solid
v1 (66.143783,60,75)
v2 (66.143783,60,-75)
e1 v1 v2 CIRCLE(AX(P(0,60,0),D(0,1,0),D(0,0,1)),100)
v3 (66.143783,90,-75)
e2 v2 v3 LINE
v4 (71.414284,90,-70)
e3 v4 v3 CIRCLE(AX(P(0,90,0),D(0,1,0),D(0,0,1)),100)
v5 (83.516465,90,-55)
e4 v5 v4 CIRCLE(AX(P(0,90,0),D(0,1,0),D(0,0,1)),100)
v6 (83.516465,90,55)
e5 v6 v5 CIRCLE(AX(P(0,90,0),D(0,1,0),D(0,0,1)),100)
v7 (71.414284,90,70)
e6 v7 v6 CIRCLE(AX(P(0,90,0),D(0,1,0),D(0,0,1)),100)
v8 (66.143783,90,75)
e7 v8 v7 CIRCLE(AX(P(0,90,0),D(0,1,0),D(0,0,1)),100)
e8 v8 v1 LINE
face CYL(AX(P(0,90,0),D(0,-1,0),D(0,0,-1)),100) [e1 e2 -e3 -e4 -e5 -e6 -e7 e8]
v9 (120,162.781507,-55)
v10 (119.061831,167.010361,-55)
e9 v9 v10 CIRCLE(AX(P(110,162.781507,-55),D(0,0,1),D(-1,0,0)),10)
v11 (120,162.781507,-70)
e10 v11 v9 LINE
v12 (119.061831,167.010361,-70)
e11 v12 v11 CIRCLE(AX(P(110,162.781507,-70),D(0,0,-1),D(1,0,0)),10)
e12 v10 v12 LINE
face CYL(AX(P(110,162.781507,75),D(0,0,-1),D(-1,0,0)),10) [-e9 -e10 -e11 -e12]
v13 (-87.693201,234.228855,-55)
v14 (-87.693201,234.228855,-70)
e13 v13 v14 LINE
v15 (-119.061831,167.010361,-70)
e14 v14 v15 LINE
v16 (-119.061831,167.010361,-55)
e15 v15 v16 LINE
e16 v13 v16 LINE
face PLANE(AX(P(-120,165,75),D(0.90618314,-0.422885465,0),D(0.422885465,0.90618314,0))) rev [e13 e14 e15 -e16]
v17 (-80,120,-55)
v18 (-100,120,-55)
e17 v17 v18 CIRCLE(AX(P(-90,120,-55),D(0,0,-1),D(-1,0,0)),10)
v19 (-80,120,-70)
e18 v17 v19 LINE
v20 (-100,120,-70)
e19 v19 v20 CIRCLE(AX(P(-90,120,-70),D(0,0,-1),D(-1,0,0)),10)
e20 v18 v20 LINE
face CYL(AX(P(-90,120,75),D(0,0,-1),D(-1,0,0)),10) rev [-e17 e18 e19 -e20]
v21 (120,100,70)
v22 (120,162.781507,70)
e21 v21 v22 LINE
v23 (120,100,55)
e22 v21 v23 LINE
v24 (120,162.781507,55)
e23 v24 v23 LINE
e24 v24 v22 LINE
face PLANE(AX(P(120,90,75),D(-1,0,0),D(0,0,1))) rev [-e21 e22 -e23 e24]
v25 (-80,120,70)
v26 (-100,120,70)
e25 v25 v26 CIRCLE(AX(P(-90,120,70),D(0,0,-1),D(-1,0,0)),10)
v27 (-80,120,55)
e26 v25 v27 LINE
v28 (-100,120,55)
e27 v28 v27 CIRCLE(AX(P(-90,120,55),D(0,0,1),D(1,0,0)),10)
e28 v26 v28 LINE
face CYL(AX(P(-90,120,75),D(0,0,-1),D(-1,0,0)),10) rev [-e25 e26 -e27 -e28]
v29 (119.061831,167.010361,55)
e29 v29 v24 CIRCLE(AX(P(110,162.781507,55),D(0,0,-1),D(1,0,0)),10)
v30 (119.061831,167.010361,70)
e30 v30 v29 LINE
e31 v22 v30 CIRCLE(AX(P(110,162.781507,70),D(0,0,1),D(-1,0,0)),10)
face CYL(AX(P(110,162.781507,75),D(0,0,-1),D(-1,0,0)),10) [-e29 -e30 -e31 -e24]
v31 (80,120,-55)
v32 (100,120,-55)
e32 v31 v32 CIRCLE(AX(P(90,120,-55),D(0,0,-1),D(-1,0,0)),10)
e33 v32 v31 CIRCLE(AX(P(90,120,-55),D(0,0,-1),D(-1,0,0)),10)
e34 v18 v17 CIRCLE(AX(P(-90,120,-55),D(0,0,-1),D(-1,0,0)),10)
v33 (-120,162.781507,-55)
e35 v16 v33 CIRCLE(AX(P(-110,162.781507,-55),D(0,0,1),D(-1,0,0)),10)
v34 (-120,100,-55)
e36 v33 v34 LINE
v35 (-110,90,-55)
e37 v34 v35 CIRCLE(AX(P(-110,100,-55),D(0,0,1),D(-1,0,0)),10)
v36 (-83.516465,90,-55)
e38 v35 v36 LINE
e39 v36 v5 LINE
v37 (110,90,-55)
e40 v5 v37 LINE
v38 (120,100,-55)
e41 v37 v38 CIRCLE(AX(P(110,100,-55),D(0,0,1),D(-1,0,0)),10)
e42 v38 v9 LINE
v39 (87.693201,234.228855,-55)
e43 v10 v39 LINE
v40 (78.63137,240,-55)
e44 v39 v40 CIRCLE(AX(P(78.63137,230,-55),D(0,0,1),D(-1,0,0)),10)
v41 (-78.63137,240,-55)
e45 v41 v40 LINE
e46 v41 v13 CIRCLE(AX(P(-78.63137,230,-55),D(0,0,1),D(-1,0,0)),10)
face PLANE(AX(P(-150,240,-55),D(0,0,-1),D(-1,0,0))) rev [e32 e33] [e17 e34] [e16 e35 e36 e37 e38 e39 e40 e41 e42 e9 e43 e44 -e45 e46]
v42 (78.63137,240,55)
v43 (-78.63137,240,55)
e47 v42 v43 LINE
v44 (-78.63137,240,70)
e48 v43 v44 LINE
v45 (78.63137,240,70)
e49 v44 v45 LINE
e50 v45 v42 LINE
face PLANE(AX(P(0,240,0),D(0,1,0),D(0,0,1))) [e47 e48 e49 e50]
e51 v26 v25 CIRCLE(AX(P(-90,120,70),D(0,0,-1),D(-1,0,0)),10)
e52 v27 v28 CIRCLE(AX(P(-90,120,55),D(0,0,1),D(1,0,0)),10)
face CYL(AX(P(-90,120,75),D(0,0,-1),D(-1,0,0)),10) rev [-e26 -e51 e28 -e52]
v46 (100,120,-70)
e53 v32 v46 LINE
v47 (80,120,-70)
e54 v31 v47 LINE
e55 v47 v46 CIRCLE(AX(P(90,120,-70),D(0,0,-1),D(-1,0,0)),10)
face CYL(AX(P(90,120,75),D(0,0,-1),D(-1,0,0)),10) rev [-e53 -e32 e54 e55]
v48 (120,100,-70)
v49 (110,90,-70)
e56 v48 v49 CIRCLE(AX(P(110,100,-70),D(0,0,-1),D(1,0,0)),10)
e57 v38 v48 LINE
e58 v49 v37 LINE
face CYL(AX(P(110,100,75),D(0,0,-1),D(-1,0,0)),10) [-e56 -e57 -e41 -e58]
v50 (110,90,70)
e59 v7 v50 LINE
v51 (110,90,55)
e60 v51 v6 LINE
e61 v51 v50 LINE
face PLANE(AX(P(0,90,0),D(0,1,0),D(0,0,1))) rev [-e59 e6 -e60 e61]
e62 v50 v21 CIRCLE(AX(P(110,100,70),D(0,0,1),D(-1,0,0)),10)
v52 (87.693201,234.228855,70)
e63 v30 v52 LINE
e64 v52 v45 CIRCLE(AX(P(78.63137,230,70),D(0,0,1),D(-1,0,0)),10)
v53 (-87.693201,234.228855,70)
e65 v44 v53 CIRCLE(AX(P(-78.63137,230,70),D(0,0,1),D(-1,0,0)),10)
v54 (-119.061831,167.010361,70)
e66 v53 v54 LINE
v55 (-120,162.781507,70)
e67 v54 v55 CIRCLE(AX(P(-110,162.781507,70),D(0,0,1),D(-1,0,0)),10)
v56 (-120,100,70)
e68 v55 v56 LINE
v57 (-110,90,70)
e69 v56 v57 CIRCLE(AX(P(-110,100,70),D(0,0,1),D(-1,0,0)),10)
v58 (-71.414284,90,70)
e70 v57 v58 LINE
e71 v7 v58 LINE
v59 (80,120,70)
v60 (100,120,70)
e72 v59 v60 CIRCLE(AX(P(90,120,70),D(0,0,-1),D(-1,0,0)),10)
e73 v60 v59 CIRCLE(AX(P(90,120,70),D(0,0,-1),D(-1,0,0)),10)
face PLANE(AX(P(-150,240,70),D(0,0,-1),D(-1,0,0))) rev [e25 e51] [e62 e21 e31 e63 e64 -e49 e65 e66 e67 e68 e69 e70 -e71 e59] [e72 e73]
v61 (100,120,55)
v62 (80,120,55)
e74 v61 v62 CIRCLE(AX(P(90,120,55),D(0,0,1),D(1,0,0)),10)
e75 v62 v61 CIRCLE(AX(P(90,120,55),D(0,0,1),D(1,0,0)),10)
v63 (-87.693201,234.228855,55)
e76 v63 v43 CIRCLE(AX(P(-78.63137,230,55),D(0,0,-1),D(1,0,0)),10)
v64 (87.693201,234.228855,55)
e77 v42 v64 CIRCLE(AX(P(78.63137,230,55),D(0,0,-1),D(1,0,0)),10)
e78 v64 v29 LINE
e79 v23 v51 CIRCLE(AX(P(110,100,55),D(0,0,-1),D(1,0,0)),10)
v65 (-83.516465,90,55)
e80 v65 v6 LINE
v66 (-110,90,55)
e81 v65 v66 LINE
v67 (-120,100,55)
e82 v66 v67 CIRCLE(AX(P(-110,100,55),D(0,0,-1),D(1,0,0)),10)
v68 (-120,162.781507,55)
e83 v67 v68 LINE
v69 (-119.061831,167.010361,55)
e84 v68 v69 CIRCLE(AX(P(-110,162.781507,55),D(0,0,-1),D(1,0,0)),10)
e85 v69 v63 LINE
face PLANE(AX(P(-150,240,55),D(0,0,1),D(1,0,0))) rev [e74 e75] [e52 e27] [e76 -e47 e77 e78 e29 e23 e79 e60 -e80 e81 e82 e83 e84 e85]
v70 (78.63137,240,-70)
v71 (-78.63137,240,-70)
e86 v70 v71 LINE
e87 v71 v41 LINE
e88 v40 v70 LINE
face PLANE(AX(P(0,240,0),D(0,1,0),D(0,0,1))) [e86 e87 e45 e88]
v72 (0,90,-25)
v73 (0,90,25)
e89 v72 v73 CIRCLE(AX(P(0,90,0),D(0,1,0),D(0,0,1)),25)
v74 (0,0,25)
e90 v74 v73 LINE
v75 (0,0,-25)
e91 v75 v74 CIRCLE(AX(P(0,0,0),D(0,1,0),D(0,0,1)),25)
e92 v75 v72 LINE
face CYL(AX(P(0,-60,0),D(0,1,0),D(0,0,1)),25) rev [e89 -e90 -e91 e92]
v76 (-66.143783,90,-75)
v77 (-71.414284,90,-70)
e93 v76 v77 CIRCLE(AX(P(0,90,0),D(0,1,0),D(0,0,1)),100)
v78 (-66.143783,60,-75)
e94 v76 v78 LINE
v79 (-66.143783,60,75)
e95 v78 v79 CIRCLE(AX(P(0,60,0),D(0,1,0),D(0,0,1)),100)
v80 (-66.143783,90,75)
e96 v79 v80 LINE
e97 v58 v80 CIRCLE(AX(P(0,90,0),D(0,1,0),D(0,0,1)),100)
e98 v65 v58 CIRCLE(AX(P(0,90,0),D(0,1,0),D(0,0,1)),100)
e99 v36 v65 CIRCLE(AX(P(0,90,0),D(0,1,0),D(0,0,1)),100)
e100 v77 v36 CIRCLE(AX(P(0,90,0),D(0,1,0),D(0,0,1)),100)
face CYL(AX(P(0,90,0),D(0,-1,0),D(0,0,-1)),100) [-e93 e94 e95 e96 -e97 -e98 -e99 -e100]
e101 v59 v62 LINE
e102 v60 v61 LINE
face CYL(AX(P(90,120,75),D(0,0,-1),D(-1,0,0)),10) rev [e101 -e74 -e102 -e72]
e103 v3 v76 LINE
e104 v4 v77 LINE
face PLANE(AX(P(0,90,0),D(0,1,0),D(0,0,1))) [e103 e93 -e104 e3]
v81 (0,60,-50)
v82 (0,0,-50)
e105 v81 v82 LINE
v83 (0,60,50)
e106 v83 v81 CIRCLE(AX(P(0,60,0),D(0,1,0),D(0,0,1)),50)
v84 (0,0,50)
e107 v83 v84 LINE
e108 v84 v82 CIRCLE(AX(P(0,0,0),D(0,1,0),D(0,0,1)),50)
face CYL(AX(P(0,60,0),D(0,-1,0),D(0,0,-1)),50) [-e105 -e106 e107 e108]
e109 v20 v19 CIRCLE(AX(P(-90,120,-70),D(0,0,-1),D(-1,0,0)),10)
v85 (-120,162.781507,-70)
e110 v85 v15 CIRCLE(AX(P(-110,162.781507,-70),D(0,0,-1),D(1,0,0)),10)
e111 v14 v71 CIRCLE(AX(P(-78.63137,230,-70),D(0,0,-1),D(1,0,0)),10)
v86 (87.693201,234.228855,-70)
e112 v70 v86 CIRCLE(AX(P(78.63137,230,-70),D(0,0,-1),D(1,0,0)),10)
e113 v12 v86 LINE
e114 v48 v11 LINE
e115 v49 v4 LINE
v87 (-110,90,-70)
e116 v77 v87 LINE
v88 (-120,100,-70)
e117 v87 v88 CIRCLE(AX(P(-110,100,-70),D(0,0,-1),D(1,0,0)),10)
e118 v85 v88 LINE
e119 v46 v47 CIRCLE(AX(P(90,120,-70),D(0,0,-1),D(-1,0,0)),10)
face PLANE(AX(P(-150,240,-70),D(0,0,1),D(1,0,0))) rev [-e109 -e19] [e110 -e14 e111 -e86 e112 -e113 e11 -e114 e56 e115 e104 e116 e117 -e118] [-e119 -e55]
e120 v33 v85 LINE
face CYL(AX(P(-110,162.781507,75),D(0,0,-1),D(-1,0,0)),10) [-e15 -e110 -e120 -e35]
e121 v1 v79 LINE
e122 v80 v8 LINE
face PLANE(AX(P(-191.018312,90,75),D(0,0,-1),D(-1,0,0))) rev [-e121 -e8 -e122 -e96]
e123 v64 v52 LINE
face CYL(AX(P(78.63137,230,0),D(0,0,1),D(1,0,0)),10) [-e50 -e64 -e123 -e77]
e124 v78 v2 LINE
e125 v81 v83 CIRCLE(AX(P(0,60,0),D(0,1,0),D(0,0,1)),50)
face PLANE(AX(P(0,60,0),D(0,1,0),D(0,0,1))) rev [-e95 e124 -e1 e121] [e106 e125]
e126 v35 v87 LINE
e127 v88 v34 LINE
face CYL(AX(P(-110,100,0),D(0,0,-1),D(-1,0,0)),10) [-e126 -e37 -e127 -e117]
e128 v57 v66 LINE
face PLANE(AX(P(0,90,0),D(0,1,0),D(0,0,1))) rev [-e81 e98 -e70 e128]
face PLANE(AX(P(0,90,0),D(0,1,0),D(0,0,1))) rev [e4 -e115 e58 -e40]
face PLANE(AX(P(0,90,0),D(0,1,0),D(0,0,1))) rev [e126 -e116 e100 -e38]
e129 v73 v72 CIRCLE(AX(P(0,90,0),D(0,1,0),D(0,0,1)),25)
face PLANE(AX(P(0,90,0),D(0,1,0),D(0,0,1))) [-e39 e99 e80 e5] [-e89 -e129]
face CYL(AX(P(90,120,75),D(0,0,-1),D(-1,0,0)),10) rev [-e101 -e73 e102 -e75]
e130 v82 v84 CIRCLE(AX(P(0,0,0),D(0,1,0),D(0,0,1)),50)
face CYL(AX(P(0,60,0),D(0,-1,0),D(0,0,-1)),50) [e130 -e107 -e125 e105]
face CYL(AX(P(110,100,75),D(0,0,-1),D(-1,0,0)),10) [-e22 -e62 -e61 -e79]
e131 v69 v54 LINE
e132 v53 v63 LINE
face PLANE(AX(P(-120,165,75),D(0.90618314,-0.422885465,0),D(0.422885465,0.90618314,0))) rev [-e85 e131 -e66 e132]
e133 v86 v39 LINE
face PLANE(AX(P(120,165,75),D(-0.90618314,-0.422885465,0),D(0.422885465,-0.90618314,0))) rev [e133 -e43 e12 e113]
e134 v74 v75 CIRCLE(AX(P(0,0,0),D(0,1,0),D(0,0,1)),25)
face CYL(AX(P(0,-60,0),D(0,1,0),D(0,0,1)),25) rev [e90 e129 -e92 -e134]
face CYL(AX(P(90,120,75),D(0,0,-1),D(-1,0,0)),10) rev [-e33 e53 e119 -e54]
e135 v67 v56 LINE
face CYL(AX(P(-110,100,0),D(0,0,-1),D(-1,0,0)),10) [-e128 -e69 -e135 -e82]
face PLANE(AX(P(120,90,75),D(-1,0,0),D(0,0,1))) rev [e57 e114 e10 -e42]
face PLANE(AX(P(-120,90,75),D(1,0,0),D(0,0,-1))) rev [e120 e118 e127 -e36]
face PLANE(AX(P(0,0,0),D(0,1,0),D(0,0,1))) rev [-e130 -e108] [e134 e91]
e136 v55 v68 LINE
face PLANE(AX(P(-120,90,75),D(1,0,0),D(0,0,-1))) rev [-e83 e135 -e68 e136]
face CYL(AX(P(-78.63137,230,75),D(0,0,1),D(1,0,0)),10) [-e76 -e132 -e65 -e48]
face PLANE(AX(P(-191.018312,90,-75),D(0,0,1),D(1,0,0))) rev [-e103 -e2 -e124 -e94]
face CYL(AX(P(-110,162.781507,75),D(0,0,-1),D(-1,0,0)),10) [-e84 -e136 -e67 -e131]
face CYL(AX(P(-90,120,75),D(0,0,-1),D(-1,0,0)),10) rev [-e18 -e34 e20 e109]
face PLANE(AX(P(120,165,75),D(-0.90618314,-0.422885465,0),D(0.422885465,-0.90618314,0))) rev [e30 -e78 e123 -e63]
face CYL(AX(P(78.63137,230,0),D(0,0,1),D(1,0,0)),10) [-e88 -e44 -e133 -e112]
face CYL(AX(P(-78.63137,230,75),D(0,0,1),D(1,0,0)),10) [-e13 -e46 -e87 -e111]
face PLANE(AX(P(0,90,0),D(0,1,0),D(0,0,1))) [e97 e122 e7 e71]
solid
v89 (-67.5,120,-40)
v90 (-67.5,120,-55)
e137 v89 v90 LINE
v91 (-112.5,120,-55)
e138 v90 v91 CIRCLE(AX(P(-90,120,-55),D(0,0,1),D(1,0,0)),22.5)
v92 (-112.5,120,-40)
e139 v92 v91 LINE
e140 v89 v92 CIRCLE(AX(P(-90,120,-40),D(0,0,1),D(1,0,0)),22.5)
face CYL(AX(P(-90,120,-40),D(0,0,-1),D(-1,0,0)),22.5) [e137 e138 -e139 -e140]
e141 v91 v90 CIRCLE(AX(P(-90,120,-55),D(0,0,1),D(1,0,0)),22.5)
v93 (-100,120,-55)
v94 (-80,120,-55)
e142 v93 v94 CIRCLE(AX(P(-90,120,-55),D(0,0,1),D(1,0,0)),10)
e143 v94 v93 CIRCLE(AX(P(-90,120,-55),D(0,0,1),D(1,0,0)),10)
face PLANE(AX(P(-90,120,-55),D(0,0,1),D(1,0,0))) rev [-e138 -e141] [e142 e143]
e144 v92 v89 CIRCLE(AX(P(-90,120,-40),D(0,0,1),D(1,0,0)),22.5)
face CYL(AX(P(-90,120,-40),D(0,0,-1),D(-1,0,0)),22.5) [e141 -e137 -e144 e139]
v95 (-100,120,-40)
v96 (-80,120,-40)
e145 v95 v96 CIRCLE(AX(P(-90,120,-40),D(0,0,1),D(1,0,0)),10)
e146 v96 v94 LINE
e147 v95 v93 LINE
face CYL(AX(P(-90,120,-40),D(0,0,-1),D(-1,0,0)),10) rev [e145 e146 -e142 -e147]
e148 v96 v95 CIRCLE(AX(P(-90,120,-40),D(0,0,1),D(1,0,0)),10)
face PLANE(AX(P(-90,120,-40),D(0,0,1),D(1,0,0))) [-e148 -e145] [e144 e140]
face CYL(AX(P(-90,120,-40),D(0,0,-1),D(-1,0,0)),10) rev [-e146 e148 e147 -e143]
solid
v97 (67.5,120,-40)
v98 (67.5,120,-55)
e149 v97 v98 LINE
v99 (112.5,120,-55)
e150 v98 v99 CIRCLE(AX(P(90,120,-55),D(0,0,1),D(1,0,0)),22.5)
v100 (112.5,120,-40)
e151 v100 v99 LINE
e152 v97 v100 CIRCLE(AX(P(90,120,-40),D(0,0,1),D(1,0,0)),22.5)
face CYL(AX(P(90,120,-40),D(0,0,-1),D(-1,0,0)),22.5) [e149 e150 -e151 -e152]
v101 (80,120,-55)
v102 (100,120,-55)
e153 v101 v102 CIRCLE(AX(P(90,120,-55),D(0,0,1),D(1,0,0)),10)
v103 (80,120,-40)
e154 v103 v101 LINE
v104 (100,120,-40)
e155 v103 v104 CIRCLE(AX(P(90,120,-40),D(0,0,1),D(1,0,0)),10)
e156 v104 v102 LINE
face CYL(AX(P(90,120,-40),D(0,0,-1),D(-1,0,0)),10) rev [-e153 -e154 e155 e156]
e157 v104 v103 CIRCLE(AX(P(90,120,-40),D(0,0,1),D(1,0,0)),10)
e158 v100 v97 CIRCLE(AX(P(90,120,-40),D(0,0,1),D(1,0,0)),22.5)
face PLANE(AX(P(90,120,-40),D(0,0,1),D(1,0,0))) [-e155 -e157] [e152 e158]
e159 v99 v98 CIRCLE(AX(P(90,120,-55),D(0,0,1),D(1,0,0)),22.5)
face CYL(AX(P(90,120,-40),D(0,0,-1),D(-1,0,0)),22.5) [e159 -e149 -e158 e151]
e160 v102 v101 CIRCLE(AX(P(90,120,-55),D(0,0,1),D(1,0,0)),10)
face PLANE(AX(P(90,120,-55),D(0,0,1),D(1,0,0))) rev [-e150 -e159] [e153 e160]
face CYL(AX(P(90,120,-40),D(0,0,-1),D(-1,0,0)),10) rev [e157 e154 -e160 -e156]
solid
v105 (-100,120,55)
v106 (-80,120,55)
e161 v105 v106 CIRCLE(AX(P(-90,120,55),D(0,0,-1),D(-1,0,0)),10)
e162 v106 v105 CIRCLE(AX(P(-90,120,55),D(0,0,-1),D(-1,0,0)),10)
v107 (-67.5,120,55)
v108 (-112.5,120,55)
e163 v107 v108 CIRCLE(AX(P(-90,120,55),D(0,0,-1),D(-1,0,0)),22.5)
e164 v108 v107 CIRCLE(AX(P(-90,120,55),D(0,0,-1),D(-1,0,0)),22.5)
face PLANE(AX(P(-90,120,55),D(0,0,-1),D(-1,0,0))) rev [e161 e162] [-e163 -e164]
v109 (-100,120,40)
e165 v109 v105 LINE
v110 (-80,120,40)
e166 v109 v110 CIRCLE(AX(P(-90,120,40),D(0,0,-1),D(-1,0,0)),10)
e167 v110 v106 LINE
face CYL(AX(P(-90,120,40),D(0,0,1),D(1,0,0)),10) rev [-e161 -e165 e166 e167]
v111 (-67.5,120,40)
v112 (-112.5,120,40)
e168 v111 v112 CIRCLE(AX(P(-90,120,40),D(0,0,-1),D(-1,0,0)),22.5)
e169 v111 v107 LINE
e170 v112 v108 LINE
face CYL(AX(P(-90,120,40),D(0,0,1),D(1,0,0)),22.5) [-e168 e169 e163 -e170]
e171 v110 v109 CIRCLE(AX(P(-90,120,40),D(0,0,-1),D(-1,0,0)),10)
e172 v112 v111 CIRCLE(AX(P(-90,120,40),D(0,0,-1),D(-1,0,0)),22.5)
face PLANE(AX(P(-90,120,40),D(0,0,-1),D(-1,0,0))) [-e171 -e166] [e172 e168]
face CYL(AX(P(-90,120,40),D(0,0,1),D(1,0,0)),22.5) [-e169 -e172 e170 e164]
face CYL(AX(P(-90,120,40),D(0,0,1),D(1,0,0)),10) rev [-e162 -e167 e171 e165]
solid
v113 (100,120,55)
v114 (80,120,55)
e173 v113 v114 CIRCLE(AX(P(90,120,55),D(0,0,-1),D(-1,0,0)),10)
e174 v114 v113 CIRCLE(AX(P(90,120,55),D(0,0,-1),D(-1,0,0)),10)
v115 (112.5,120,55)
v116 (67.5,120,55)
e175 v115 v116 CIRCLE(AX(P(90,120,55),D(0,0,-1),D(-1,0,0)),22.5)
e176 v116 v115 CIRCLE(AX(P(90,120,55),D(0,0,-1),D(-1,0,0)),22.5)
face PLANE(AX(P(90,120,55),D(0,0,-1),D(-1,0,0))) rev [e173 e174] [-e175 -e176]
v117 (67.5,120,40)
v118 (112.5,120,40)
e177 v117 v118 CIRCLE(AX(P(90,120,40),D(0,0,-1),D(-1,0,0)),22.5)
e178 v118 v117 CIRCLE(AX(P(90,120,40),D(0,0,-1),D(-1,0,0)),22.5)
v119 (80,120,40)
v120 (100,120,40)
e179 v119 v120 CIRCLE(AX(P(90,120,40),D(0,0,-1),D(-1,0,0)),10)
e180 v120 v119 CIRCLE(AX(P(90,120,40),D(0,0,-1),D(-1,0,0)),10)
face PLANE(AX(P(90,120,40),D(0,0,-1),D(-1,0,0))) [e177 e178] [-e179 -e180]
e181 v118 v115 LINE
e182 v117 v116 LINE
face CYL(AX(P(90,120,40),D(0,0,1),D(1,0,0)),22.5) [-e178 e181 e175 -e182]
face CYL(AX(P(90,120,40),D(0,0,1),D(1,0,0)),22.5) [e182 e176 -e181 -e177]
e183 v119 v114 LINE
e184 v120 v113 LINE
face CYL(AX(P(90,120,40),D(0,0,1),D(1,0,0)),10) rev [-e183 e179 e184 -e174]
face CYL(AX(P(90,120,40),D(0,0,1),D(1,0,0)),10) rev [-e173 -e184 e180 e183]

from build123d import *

# Parameters (mm, degrees)
SKETCH1_R             = 50
BOSS_EXTRUDE1_DEPTH   = 60
SKETCH2_R             = 100
BOSS_EXTRUDE2_DEPTH   = 30
CUT_EXTRUDE1_DEPTH    = 154.622914957
SKETCH4_W             = 300
SKETCH4_H             = 15
BOSS_EXTRUDE3_DEPTH   = 150
SKETCH5_W             = 30
SKETCH5_H             = 150
CUT_EXTRUDE2_DEPTH    = 319.001572323
FILLET1_R             = 10
SKETCH6_R             = 25
CUT_EXTRUDE3_DEPTH    = 150
SKETCH7_R             = 10
CUT_EXTRUDE4_DEPTH    = 306
SKETCH8_R             = 22.5
SKETCH8_R_2           = 10
BOSS_EXTRUDE4_DEPTH   = 15
BOSS_EXTRUDE4_2_DEPTH = 15
SKETCH9_R             = 22.5
SKETCH9_R_2           = 10
BOSS_EXTRUDE5_DEPTH   = 15
BOSS_EXTRUDE5_2_DEPTH = 15
CUT_EXTRUDE5_DEPTH    = 306
FILLET2_R             = 10


with BuildPart() as part:
    # Sketch1 → Boss-Extrude1 (new body)
    with BuildSketch(Plane(origin=(0, 0, 0), x_dir=(1, 0, 0), z_dir=(0, 1, 0))):
        with Locations(Location((0, 0, 0), (0, 0, 270))):
            Circle(SKETCH1_R)
    extrude(amount=BOSS_EXTRUDE1_DEPTH)

    # Sketch2 → Boss-Extrude2 (add)
    with BuildSketch(Plane(origin=(0, 60, 0), x_dir=(1, 0, 0), z_dir=(0, 1, 0))):
        with Locations(Location((0, 0, 0), (0, 0, 270))):
            Circle(SKETCH2_R)
    extrude(amount=BOSS_EXTRUDE2_DEPTH)

    # Sketch3 → Cut-Extrude1 (cut, through all)
    with BuildSketch(Plane.XZ.offset(-60)):
        Polygon((191.018311805, 75), (5.81663556, 170.543754632), (-191.018311805, 75), align=None)
        Polygon((-191.018311805, -75), (191.018311805, -75), (12.796598233, -157.049160132), align=None)
    extrude(amount=-CUT_EXTRUDE1_DEPTH, mode=Mode.SUBTRACT)

    # Sketch4 → Boss-Extrude3 (add)
    with BuildSketch(Plane(origin=(0, 90, 0), x_dir=(1, 0, 0), z_dir=(0, 1, 0))):
        with Locations((0, 62.5)):
            Rectangle(SKETCH4_W, SKETCH4_H)
        with Locations((0, -62.5)):
            Rectangle(SKETCH4_W, SKETCH4_H)
    extrude(amount=BOSS_EXTRUDE3_DEPTH)

    # Sketch5 → Cut-Extrude2 (cut, through all)
    with BuildSketch(Plane(origin=(0, 0, -70), x_dir=(-1, 0, 0), z_dir=(0, 0, -1))):
        with Locations((-135, 165)):
            Rectangle(SKETCH5_W, SKETCH5_H)
        with Locations((135, 165)):
            Rectangle(SKETCH5_W, SKETCH5_H)
    extrude(amount=-CUT_EXTRUDE2_DEPTH, mode=Mode.SUBTRACT)

    # Fillet1
    fillet1_edges = [part.edges().sort_by_distance(p)[0] for p in [
        (-120, 240, -62.5),
        (-120, 240, 62.5),
        (-120, 90, -62.5),
        (-120, 90, 62.5),
        (120, 240, 62.5),
        (120, 90, -62.5),
        (120, 90, 62.5),
        (120, 240, -62.5),
    ]]
    fillet(fillet1_edges, radius=FILLET1_R)

    # Sketch6 → Cut-Extrude3 (cut)
    with BuildSketch(Plane(origin=(0, 90, 0), x_dir=(1, 0, 0), z_dir=(0, 1, 0))):
        with Locations(Location((0, 0, 0), (0, 0, 270))):
            Circle(SKETCH6_R)
    extrude(amount=-CUT_EXTRUDE3_DEPTH, mode=Mode.SUBTRACT)

    # Sketch7 → Cut-Extrude4 (cut, through all)
    with BuildSketch(Plane(origin=(0, 0, -70), x_dir=(-1, 0, 0), z_dir=(0, 0, -1))):
        with Locations((-90, 120)):
            Circle(SKETCH7_R)
        with Locations((90, 120)):
            Circle(SKETCH7_R)
    extrude(amount=-CUT_EXTRUDE4_DEPTH, mode=Mode.SUBTRACT)

    # Sketch10 → Cut-Extrude5 (cut, through all)
    with BuildSketch(Plane(origin=(0, 0, -70), x_dir=(-1, 0, 0), z_dir=(0, 0, -1))):
        Polygon((-120, 165), (-85, 240), (-120, 240), align=None)
        Polygon((120, 165), (85, 240), (120, 240), align=None)
    extrude(amount=-CUT_EXTRUDE5_DEPTH, mode=Mode.SUBTRACT)

    # Fillet2
    fillet2_edges = [part.edges().sort_by_distance(p)[0] for p in [
        (85, 240, -62.5),
        (85, 240, 62.5),
        (120, 165, 62.5),
        (120, 165, -62.5),
        (-120, 165, -62.5),
        (-120, 165, 62.5),
        (-85, 240, 62.5),
        (-85, 240, -62.5),
    ]]
    fillet(fillet2_edges, radius=FILLET2_R)


with BuildPart() as body_2:
    # Sketch8 → Boss-Extrude4 (new body)
    with BuildSketch(Plane(origin=(0, 0, 55), x_dir=(-1, 0, 0), z_dir=(0, 0, -1))):
        with Locations((90, 120)):
            Circle(SKETCH8_R)
        with Locations((90, 120)):
            Circle(SKETCH8_R_2, mode=Mode.SUBTRACT)
    extrude(amount=BOSS_EXTRUDE4_DEPTH)


with BuildPart() as body_3:
    # Sketch8 → Boss-Extrude4 2 (new body)
    with BuildSketch(Plane(origin=(0, 0, 55), x_dir=(-1, 0, 0), z_dir=(0, 0, -1))):
        with Locations((-90, 120)):
            Circle(SKETCH8_R)
        with Locations((-90, 120)):
            Circle(SKETCH8_R_2, mode=Mode.SUBTRACT)
    extrude(amount=BOSS_EXTRUDE4_2_DEPTH)


with BuildPart() as body_4:
    # Sketch9 → Boss-Extrude5 (new body)
    with BuildSketch(Plane.XY.offset(-55)):
        with Locations((90, 120)):
            Circle(SKETCH9_R)
        with Locations((90, 120)):
            Circle(SKETCH9_R_2, mode=Mode.SUBTRACT)
    extrude(amount=BOSS_EXTRUDE5_DEPTH)


with BuildPart() as body_5:
    # Sketch9 → Boss-Extrude5 2 (new body)
    with BuildSketch(Plane.XY.offset(-55)):
        with Locations((-90, 120)):
            Circle(SKETCH9_R)
        with Locations((-90, 120)):
            Circle(SKETCH9_R_2, mode=Mode.SUBTRACT)
    extrude(amount=BOSS_EXTRUDE5_2_DEPTH)


solid = Compound([part.part, body_2.part, body_3.part, body_4.part, body_5.part])
